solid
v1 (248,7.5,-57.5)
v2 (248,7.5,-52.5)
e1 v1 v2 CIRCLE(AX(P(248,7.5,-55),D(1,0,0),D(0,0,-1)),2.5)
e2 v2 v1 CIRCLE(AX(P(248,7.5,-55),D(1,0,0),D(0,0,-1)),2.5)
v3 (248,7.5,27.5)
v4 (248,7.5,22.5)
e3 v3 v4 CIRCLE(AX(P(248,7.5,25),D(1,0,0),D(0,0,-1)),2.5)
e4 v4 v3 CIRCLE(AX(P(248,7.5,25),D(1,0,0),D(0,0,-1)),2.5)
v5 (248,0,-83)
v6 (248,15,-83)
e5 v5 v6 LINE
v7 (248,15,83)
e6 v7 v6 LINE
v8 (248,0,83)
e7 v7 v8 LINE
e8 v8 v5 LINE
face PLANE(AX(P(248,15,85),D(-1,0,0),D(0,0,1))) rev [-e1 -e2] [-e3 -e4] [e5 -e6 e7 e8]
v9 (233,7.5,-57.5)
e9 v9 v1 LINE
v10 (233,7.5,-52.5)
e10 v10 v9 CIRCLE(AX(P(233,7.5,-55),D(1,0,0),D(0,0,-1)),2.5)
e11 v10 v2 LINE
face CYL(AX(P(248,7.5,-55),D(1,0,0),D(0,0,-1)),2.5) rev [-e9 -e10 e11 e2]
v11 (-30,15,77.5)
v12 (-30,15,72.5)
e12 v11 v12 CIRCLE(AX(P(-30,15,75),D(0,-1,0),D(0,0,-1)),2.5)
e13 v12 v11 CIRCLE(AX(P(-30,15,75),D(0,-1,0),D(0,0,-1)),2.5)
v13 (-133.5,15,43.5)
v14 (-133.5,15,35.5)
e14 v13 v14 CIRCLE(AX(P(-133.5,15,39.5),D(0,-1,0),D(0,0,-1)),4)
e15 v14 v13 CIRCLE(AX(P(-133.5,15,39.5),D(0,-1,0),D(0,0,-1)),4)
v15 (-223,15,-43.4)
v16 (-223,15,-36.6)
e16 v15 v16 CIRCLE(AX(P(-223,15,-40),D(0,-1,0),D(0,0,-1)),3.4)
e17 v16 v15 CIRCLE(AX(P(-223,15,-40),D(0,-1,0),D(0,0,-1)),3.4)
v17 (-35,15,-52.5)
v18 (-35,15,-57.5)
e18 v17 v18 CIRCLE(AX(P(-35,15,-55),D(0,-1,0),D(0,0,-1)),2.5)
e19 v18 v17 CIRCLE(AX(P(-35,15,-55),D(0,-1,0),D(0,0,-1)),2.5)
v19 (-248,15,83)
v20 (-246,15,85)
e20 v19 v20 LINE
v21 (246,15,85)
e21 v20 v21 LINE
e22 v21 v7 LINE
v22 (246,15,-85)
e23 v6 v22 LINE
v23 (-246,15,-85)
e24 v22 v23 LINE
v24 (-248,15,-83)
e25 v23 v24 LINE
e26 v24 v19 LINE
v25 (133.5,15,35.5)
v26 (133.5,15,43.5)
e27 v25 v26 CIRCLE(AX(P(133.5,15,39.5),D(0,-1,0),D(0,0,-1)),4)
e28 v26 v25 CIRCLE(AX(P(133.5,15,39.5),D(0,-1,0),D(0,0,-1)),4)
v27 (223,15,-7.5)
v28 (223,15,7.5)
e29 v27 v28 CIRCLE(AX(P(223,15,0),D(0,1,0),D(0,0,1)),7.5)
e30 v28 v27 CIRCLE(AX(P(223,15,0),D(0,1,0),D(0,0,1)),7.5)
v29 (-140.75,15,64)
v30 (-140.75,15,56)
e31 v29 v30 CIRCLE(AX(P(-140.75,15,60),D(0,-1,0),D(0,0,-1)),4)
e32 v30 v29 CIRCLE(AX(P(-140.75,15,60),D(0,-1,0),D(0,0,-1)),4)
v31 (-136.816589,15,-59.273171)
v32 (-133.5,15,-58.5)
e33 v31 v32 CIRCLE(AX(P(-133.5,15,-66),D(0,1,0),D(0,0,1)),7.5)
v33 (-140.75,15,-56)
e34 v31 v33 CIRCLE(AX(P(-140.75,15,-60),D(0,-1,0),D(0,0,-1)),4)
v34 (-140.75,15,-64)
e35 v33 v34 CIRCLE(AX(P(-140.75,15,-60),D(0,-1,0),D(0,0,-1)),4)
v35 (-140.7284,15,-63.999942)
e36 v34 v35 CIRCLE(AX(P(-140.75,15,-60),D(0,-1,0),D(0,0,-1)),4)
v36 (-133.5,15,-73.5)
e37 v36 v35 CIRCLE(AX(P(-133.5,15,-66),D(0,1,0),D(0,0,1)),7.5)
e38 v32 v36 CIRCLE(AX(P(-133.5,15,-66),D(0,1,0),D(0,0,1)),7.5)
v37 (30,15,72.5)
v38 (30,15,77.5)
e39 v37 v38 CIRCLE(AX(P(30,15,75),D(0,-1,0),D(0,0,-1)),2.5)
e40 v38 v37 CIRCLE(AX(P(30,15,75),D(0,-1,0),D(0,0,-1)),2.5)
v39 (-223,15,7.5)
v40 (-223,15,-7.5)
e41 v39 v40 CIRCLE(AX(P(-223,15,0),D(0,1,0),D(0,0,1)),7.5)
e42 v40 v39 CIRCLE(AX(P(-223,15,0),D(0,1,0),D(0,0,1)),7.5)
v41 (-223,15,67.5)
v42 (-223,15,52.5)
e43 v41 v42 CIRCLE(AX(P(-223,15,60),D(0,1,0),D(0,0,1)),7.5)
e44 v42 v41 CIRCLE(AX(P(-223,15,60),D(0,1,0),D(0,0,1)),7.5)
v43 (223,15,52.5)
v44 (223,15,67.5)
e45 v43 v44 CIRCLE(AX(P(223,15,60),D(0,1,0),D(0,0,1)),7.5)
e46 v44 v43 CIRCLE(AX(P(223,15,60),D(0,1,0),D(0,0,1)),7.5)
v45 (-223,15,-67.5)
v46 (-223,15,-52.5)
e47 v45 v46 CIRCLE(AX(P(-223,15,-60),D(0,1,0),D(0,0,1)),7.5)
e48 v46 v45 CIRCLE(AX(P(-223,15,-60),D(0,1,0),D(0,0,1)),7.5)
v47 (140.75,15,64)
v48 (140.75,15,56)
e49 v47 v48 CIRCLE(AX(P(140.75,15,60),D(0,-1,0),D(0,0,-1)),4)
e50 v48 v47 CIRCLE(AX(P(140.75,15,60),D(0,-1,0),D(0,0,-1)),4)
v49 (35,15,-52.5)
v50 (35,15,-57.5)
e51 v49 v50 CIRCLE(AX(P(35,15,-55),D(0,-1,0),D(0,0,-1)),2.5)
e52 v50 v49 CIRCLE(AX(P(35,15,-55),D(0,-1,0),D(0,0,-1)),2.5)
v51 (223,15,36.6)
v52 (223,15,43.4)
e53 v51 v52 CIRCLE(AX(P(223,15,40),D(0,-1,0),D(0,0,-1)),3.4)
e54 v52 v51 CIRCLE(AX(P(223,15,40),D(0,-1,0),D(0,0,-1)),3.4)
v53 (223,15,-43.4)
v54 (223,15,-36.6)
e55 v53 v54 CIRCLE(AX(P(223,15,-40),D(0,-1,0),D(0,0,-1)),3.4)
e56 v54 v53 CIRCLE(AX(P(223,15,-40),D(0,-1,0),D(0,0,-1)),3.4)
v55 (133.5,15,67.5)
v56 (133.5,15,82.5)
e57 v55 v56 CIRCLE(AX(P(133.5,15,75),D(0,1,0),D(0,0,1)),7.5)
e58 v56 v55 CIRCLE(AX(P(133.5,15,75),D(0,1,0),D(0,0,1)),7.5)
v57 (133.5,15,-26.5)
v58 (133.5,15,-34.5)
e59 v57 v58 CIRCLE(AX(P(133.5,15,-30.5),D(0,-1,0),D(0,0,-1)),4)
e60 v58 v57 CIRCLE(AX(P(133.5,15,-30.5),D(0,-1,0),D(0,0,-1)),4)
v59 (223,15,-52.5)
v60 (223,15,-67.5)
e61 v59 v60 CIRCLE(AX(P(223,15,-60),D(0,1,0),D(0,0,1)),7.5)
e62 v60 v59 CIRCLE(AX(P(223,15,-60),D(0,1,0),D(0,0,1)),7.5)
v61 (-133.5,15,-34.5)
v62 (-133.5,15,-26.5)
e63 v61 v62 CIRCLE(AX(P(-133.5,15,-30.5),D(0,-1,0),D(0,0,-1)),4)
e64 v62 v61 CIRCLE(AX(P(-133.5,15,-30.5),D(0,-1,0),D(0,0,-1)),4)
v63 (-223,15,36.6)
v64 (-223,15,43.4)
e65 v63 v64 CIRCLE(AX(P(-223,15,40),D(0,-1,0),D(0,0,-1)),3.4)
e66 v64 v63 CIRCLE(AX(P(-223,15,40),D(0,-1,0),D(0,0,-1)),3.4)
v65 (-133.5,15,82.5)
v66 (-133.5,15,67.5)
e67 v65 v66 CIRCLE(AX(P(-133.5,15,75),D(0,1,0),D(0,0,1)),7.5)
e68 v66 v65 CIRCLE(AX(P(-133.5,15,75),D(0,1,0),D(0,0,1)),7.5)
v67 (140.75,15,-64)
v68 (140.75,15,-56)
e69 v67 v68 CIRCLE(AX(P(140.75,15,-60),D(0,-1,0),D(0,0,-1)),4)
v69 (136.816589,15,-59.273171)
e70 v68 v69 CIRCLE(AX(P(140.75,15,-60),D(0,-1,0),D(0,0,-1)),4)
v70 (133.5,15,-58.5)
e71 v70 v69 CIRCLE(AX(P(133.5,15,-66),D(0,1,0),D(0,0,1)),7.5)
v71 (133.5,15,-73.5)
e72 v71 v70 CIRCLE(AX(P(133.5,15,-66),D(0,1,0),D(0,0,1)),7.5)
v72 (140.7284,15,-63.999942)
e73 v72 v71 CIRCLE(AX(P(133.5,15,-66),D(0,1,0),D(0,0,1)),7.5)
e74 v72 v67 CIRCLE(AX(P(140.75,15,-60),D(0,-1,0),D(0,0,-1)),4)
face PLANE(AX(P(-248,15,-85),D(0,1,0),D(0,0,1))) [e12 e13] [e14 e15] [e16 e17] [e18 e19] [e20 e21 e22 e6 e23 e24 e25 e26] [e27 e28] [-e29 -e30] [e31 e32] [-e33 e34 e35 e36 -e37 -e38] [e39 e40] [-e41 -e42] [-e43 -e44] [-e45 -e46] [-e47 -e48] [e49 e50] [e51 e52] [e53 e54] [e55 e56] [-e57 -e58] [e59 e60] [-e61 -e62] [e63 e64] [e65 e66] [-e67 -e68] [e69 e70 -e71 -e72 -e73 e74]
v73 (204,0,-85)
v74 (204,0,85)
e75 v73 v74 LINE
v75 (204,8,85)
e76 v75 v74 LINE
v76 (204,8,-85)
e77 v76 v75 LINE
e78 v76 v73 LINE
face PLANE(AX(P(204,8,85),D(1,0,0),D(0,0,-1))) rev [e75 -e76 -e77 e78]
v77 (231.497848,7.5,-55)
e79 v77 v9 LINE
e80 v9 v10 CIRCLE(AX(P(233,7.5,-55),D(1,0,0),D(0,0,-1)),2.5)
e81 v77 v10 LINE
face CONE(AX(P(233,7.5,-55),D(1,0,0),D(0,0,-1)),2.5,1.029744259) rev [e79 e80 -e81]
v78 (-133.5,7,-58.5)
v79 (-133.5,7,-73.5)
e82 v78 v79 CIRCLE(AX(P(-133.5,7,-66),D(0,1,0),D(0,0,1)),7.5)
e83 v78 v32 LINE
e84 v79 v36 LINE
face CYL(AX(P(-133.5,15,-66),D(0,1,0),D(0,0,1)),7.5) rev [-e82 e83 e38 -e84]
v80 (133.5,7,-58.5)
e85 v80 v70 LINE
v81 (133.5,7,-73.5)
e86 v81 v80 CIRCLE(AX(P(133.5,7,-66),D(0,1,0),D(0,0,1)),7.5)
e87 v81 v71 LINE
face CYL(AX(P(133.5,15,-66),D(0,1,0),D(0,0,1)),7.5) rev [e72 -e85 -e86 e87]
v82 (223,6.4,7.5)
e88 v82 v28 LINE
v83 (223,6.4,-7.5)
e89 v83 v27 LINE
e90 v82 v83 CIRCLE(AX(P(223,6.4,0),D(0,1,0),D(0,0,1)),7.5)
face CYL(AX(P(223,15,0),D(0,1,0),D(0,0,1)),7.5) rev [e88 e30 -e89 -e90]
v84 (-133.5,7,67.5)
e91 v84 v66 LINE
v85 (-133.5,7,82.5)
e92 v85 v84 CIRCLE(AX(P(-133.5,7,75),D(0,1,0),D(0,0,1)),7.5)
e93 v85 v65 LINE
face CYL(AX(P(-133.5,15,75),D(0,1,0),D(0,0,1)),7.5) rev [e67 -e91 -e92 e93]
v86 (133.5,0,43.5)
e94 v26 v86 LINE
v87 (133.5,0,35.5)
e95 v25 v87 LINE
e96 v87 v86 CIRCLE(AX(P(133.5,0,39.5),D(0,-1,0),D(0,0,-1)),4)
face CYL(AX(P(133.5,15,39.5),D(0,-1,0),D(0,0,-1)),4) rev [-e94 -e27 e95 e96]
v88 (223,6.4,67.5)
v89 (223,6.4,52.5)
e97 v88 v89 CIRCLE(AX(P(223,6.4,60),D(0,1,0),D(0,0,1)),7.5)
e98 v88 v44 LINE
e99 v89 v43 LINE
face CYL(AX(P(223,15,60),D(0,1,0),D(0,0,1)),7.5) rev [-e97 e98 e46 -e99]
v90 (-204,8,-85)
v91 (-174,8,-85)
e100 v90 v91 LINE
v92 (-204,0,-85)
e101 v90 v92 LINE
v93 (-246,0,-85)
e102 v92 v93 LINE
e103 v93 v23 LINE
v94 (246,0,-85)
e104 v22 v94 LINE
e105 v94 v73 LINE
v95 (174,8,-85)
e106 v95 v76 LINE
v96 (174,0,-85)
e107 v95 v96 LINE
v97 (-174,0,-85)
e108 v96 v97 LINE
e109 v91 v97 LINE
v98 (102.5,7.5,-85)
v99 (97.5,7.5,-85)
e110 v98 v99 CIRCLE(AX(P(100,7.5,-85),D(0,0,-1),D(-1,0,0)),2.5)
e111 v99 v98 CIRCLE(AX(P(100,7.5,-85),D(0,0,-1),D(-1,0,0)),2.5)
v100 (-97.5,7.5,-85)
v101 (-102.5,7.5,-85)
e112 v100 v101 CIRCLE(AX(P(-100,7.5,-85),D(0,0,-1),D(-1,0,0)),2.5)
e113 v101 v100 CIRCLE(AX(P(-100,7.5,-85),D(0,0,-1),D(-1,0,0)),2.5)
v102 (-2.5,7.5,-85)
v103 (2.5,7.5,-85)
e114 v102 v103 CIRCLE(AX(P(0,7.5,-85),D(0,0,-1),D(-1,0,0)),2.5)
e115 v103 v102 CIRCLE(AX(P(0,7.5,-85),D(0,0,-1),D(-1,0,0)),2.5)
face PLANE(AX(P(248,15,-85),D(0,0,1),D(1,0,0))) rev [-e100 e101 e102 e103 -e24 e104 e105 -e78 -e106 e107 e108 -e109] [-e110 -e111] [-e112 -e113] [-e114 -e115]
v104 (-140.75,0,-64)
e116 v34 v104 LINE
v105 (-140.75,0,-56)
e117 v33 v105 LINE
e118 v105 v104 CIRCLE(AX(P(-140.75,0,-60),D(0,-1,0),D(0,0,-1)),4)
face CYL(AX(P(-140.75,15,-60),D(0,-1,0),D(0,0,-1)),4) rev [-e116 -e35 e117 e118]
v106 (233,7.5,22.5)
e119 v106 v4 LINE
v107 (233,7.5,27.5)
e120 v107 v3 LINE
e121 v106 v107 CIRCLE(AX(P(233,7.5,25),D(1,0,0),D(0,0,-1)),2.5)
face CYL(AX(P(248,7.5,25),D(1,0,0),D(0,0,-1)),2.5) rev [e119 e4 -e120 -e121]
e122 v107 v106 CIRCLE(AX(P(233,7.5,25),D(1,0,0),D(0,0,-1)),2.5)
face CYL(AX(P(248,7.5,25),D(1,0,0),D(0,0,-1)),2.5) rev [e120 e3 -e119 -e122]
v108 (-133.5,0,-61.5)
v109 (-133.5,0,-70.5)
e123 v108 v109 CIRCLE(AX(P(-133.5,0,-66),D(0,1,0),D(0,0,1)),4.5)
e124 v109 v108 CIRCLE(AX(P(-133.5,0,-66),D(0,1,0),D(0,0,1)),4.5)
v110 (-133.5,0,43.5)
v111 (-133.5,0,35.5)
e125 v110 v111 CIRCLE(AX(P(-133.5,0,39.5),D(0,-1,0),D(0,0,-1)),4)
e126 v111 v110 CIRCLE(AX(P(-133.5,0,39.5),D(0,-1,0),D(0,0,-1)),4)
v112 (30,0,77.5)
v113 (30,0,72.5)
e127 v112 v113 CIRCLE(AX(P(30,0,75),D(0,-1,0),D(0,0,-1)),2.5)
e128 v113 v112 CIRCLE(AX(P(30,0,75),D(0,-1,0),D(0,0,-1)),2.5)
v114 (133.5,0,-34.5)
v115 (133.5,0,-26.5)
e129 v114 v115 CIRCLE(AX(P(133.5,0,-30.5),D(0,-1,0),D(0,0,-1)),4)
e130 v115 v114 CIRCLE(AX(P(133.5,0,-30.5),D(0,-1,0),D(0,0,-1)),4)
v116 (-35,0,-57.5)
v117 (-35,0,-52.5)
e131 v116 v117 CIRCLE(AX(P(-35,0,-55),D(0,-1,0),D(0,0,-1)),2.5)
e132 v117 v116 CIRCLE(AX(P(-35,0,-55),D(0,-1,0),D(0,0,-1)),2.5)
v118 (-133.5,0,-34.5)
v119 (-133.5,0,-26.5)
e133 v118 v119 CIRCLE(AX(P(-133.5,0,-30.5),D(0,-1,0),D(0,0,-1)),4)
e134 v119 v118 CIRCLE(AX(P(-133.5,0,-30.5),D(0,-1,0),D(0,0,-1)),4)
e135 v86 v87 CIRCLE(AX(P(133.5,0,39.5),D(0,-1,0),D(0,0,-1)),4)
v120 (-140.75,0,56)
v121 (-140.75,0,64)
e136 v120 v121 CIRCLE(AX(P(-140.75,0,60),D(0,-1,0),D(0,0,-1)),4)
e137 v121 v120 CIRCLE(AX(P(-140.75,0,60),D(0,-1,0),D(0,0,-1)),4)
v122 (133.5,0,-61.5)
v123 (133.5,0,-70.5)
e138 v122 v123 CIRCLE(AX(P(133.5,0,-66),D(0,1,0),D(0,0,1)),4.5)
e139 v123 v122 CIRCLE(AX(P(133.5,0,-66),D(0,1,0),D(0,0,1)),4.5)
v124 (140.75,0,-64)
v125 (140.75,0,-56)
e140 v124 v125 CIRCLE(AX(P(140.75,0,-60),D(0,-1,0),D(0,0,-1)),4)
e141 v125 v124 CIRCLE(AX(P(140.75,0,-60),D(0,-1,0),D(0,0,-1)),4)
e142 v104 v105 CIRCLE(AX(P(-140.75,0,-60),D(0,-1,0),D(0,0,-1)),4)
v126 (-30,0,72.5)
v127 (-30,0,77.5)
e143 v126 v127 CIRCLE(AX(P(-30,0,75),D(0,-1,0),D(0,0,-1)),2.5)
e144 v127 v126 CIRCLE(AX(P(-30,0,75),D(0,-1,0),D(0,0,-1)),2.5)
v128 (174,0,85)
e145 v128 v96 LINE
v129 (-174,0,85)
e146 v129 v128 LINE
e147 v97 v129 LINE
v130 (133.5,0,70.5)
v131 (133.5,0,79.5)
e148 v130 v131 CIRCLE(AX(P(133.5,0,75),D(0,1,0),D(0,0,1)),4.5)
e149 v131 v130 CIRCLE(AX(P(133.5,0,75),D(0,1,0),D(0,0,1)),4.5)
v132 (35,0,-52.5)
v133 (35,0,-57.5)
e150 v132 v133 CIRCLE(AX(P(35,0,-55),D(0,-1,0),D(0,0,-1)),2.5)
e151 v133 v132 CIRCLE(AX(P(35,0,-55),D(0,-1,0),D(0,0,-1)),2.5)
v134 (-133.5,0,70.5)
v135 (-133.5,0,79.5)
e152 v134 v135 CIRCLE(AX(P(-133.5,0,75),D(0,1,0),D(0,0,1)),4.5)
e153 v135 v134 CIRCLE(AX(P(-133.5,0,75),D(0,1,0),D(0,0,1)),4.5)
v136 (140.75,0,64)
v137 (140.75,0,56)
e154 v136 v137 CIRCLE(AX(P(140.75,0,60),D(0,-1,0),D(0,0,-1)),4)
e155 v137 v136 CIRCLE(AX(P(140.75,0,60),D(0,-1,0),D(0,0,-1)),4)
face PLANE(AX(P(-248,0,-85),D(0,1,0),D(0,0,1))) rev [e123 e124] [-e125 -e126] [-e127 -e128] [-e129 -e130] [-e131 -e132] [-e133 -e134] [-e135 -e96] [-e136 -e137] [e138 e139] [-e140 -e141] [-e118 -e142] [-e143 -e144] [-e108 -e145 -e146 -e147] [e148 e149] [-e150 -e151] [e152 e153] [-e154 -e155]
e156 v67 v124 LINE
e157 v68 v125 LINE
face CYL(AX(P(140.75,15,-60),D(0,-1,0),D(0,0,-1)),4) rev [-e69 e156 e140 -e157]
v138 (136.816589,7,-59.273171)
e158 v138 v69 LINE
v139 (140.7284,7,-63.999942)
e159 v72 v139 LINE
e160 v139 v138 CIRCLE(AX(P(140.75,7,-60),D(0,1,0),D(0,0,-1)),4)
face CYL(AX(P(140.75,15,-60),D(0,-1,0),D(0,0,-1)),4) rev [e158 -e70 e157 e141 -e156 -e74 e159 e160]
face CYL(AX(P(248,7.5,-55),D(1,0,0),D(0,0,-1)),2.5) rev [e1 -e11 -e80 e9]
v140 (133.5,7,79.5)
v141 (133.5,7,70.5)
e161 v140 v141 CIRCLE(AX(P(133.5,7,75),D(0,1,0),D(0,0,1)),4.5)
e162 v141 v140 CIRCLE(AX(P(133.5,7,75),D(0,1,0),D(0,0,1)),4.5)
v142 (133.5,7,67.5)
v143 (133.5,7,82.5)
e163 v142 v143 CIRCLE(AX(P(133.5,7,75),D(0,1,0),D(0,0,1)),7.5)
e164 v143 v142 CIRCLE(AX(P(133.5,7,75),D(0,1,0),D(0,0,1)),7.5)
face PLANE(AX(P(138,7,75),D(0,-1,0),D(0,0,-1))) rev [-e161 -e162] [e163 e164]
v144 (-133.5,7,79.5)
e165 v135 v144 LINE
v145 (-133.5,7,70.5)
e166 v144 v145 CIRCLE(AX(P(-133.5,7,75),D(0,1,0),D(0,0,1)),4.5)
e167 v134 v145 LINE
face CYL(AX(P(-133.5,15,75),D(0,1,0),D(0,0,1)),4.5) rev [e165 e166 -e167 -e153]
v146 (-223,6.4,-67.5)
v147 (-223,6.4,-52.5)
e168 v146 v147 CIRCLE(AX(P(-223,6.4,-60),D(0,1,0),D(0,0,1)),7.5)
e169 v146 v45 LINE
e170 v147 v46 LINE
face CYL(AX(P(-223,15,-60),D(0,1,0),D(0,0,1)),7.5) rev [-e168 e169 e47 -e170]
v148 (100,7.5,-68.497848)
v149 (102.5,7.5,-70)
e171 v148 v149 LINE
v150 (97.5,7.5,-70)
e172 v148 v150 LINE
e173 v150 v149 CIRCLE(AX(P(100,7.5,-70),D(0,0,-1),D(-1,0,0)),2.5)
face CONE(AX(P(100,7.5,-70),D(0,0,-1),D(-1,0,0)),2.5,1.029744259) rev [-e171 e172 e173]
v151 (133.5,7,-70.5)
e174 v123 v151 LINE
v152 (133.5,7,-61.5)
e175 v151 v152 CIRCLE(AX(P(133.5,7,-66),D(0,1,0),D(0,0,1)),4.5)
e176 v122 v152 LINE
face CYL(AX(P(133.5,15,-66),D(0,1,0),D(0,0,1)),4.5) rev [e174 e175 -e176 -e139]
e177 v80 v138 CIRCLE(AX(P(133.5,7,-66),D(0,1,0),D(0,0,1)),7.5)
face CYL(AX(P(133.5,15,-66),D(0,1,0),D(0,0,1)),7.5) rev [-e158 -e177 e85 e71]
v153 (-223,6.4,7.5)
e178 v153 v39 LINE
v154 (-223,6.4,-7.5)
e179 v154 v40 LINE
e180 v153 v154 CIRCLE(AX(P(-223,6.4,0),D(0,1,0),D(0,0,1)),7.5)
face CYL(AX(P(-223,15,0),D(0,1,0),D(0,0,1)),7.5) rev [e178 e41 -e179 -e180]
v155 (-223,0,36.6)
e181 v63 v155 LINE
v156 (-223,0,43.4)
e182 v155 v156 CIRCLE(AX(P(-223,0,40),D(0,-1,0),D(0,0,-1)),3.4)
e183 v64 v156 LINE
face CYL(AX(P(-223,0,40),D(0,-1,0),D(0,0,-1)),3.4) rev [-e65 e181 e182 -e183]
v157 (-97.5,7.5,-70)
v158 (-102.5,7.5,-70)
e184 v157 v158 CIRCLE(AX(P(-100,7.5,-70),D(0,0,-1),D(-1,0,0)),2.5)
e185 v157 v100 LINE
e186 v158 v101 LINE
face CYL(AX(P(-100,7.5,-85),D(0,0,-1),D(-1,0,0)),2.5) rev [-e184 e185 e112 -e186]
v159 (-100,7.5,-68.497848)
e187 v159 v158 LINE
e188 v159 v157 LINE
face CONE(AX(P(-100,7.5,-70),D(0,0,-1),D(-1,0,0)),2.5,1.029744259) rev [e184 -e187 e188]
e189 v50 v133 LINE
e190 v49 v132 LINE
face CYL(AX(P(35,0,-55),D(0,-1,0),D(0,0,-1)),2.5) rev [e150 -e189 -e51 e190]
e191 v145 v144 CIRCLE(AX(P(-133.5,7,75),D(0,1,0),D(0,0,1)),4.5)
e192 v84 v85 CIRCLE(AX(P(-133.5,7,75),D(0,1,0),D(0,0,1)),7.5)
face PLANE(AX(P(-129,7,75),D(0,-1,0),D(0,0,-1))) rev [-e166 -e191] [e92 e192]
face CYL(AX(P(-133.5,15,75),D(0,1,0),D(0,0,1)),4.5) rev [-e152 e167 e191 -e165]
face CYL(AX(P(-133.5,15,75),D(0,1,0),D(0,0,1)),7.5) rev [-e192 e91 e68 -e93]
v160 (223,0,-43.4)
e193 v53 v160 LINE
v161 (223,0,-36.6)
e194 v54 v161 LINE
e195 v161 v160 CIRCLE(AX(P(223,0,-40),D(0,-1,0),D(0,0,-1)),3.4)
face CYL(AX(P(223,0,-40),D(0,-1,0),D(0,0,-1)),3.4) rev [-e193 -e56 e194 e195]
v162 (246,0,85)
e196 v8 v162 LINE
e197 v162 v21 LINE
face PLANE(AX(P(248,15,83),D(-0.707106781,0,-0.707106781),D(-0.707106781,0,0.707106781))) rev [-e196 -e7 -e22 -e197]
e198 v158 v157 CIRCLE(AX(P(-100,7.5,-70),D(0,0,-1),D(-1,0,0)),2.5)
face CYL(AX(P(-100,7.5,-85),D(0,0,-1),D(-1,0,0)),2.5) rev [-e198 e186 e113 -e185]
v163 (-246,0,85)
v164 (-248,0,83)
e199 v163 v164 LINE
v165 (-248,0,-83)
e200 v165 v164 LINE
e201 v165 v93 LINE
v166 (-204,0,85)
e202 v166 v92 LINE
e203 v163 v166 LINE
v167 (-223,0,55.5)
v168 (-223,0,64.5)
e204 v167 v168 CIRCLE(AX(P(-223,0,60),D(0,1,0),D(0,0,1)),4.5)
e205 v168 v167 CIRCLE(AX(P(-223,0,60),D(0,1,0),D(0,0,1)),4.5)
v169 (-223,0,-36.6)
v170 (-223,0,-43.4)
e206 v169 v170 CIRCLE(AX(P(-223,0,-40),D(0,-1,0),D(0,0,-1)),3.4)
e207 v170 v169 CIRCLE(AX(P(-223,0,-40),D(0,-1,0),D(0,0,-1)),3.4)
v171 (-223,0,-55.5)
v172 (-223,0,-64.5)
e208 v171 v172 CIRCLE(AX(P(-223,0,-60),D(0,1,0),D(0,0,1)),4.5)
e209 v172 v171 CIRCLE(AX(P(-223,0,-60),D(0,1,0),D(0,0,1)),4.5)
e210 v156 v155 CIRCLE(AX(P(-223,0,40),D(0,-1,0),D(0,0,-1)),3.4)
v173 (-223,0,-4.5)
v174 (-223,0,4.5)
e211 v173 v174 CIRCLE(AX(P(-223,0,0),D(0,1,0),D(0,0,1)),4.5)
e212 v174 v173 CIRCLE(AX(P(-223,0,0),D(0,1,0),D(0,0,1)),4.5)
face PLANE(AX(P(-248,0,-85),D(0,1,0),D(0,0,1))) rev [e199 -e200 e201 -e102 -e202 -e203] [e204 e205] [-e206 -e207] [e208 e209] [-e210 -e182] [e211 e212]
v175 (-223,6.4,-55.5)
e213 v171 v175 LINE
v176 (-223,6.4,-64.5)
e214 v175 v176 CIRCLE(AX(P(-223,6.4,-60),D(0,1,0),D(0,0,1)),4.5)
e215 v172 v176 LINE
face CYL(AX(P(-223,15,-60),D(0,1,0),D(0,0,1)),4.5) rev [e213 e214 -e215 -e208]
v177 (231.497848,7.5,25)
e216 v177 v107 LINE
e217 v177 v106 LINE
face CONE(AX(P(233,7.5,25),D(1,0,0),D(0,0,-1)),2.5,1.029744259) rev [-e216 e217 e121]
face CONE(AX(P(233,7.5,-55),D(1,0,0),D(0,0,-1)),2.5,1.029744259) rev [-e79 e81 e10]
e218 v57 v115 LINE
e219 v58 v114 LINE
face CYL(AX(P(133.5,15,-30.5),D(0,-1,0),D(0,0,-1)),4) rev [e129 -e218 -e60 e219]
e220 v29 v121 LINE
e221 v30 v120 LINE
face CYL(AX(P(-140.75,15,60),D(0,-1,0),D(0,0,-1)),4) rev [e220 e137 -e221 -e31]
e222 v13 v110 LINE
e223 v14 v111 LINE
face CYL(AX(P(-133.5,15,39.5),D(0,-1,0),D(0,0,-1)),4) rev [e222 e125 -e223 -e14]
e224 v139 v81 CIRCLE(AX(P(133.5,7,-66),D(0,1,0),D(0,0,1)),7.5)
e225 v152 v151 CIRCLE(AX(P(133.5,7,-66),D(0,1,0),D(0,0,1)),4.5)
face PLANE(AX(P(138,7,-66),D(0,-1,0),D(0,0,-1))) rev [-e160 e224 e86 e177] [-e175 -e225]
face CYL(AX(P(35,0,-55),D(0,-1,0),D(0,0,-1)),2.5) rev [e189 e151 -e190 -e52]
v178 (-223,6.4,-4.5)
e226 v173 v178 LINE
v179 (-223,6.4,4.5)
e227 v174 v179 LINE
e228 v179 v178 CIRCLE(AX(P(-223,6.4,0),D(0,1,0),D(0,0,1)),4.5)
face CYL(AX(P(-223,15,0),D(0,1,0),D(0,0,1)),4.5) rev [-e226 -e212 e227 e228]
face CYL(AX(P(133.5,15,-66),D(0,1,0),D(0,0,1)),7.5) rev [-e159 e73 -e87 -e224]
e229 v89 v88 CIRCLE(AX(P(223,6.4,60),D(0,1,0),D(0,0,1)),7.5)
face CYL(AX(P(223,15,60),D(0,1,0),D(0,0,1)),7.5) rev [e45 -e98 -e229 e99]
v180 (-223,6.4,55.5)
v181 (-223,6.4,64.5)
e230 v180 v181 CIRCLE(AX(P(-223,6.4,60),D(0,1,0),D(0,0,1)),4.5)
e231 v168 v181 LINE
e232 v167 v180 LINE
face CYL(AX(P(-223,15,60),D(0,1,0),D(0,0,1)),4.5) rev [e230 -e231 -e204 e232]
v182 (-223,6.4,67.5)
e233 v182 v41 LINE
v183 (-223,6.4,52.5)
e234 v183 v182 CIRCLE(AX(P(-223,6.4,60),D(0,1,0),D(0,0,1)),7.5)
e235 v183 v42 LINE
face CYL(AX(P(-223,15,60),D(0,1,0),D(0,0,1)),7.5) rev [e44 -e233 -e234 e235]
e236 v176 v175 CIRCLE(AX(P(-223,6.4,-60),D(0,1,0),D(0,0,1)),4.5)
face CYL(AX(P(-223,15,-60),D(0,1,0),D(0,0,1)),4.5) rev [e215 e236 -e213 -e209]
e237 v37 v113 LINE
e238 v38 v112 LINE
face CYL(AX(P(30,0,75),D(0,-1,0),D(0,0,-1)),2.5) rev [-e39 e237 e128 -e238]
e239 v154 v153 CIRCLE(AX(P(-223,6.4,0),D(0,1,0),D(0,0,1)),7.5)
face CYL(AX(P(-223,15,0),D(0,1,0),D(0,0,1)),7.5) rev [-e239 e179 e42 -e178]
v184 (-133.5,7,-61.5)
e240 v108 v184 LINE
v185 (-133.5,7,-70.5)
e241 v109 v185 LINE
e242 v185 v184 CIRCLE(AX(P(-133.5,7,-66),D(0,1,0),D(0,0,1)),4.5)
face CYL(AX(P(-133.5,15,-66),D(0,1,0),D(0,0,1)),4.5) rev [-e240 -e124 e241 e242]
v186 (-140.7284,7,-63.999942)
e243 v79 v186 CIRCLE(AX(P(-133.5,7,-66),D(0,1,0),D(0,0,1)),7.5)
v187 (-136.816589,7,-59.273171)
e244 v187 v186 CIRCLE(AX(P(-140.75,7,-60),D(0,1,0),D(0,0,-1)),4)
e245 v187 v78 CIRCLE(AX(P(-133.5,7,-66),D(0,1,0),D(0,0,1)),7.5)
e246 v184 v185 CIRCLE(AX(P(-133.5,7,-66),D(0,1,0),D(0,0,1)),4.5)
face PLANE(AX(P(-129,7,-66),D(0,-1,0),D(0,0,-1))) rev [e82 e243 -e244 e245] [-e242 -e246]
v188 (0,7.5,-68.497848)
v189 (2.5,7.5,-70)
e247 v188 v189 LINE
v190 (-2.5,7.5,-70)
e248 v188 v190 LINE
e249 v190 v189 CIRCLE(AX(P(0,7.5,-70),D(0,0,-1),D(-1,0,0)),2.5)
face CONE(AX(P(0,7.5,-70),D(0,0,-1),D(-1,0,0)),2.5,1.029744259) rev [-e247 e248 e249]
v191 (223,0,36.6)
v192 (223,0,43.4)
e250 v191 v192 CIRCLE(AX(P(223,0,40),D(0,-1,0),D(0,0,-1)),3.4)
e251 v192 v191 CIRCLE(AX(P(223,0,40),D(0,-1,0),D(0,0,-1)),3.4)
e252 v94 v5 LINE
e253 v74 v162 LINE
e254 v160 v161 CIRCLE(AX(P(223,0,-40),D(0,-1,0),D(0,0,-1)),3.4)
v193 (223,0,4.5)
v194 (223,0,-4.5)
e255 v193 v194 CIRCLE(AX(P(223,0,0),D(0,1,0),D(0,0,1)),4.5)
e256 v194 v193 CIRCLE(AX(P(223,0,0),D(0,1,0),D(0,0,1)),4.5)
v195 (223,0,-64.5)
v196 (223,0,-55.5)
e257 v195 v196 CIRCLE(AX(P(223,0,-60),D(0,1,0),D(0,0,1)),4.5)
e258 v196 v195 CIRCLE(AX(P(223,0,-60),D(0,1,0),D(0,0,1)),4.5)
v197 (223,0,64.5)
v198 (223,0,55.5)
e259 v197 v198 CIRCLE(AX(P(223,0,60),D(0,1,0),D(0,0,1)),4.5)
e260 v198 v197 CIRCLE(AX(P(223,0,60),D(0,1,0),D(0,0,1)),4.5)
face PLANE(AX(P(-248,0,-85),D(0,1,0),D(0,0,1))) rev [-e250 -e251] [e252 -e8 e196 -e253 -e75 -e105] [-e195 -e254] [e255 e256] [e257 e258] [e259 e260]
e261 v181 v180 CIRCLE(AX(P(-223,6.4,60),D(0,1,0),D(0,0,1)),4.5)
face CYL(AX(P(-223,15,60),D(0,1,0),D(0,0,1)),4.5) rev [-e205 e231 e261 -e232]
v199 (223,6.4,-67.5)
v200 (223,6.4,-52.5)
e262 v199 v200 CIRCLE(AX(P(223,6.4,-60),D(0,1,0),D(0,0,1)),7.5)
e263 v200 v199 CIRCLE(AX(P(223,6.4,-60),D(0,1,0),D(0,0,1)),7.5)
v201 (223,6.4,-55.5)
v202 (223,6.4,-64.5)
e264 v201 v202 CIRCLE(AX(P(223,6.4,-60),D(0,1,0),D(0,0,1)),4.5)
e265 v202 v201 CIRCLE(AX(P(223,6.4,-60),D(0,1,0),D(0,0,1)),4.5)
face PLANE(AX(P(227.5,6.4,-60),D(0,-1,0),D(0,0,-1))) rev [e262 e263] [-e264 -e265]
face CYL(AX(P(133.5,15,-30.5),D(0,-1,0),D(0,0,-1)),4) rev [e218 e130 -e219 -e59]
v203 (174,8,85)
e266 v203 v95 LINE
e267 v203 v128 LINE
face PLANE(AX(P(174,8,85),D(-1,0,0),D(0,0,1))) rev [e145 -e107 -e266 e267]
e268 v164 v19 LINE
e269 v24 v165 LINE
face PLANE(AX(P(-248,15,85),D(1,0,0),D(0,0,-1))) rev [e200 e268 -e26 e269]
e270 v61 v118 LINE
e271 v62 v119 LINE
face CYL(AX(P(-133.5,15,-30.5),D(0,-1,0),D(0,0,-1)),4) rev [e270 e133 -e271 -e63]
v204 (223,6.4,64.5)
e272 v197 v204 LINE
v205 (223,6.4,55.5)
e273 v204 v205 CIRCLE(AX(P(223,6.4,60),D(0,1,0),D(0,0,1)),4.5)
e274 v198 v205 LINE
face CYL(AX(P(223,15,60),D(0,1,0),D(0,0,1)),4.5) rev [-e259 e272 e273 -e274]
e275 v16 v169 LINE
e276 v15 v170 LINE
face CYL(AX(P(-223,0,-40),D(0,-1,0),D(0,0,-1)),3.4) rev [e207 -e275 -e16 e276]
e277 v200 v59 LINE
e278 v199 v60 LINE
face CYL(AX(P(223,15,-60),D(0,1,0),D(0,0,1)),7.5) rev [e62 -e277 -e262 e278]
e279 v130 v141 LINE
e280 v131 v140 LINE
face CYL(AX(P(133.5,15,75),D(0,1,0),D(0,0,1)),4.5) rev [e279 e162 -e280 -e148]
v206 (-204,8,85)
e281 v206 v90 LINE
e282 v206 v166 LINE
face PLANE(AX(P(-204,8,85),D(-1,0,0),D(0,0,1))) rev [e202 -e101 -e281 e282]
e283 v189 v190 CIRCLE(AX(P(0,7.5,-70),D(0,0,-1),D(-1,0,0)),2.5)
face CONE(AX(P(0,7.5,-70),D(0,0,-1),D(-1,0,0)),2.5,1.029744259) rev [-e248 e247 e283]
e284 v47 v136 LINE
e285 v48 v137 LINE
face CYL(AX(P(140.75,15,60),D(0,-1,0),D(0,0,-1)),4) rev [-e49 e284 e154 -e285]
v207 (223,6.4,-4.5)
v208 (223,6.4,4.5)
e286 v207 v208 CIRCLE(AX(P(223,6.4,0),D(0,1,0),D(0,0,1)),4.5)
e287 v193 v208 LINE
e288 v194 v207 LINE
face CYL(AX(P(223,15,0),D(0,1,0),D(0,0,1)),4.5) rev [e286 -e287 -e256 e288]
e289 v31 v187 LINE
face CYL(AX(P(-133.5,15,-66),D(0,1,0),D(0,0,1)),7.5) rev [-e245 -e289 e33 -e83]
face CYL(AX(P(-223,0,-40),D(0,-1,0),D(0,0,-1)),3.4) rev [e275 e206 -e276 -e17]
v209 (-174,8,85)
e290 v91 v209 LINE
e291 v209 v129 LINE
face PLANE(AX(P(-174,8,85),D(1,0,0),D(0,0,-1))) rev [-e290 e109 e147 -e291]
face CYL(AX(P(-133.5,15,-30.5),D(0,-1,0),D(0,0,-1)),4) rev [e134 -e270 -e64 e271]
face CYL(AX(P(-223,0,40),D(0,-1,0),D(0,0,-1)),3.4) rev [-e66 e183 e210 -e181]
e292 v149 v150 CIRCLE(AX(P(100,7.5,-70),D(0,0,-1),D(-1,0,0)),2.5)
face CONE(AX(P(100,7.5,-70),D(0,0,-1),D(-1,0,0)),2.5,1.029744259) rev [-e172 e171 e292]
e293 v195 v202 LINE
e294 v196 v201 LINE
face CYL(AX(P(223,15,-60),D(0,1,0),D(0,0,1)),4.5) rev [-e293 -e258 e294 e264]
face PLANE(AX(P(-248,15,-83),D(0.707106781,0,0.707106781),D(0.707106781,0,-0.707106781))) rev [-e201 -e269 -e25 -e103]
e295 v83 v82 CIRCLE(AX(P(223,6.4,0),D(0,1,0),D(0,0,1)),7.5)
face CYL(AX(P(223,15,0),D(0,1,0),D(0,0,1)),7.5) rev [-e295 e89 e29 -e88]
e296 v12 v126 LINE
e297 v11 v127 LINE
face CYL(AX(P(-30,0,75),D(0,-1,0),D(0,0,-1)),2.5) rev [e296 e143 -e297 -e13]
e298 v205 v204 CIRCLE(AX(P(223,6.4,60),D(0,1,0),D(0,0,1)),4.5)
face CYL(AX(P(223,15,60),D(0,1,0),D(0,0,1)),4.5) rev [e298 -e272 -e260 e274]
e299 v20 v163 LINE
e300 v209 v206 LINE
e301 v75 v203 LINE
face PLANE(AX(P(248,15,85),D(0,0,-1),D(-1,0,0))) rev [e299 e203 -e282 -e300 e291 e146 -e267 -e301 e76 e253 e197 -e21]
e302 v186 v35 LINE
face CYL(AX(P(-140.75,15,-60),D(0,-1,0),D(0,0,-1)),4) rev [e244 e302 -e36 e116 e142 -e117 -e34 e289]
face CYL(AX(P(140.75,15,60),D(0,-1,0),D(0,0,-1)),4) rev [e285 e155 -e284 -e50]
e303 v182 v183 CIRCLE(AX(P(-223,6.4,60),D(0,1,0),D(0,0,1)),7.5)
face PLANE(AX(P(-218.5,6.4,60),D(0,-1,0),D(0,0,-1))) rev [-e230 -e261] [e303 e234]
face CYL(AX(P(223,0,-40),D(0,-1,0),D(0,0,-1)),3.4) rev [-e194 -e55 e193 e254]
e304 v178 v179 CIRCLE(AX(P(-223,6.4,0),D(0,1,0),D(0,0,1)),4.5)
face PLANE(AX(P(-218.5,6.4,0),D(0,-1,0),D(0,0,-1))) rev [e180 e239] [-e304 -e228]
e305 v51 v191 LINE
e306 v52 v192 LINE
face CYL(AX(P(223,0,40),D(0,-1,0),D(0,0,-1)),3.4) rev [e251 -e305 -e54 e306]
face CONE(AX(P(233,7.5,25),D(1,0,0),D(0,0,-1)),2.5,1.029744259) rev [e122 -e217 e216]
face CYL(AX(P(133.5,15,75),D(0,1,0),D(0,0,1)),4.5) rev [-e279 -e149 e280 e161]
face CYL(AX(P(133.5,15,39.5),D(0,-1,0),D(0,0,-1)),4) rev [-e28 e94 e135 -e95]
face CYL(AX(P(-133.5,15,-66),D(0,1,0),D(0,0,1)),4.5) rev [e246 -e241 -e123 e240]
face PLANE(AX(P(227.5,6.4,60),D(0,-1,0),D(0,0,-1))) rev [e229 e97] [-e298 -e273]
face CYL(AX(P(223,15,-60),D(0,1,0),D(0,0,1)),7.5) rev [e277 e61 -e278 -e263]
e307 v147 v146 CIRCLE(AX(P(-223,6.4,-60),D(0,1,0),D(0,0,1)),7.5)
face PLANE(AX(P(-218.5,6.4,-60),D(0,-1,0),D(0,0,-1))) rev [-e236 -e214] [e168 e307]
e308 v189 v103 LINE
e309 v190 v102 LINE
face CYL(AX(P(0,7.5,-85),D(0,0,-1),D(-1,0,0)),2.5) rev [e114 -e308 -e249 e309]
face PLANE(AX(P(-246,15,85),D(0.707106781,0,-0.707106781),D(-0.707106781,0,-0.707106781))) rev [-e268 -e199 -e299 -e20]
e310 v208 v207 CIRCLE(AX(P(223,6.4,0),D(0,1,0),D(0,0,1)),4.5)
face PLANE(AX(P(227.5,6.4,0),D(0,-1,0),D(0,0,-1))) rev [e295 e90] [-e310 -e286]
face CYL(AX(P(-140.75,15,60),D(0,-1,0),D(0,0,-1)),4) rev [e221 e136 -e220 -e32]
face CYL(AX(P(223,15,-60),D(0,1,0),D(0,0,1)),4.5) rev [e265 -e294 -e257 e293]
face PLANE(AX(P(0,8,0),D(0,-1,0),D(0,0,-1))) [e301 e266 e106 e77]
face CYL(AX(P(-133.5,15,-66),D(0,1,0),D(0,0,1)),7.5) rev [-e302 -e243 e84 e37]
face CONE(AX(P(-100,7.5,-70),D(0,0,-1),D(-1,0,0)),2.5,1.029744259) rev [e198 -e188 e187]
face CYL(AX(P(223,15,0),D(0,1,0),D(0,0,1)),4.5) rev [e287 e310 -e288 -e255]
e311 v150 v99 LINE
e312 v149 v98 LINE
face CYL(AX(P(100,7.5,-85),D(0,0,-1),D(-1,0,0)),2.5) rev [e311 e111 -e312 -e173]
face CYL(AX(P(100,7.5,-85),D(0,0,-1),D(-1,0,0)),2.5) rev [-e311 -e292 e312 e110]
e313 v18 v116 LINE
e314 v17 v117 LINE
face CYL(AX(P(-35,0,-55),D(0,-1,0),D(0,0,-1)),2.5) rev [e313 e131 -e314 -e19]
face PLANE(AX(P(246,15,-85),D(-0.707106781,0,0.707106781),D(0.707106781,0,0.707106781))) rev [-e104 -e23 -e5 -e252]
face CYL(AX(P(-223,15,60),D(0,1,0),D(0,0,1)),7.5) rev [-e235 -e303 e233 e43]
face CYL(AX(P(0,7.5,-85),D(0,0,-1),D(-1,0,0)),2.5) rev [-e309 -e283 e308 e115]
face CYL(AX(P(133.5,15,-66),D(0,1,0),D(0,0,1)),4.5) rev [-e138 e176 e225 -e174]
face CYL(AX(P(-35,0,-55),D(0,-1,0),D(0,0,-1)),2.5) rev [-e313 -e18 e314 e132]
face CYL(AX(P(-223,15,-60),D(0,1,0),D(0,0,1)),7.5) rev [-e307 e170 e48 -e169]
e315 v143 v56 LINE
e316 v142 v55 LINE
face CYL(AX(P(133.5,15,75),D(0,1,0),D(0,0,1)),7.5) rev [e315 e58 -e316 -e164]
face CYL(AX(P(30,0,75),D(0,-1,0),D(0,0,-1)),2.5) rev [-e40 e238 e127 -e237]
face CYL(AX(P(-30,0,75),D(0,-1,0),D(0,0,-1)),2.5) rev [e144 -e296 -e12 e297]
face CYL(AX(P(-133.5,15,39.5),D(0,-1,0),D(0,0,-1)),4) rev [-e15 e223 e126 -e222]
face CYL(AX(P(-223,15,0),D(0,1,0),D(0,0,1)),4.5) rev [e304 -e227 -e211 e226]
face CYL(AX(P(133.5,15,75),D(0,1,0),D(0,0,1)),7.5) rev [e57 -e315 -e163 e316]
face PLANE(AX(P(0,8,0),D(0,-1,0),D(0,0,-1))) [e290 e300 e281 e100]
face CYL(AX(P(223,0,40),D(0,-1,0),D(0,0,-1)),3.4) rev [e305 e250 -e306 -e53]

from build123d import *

# Parameters (mm, degrees)
SKETCH1_W                                           = 496
SKETCH1_H                                           = 170
BOSS_EXTRUDE1_DEPTH                                 = 15
CBORE_FOR_M8_HEX_SOCKET_HEAD_CAP_SCREW2_D           = 9
CBORE_FOR_M8_HEX_SOCKET_HEAD_CAP_SCREW2_CBORE_D     = 15
CBORE_FOR_M8_HEX_SOCKET_HEAD_CAP_SCREW2_CBORE_DEPTH = 8.6
SKETCH4_R                                           = 4
CUT_EXTRUDE1_DEPTH                                  = 263.59093663
SKETCH5_R                                           = 4
CUT_EXTRUDE2_DEPTH                                  = 263.59093663
CBORE_FOR_M8_HEX_SOCKET_HEAD_CAP_SCREW1_D           = 9
CBORE_FOR_M8_HEX_SOCKET_HEAD_CAP_SCREW1_CBORE_D     = 15
CBORE_FOR_M8_HEX_SOCKET_HEAD_CAP_SCREW1_CBORE_DEPTH = 8
M6_TAPPED_HOLE1_D                                   = 5
M6_TAPPED_HOLE1_DEPTH                               = 15
M6_TAPPED_HOLE1_TIP                                 = 1.502151548
M6_TAPPED_HOLE2_D                                   = 5
CHAMFER1_SIZE                                       = 2
M6_TAPPED_HOLE3_D                                   = 5
M6_TAPPED_HOLE4_D                                   = 5
M6_TAPPED_HOLE4_DEPTH                               = 15
M6_TAPPED_HOLE4_TIP                                 = 1.502151548
M8_TAPPED_HOLE1_D                                   = 6.8
SKETCH18_W                                          = 30
SKETCH18_H                                          = 170
CUT_EXTRUDE3_DEPTH                                  = 8


with BuildPart() as part:
    # Sketch1 → Boss-Extrude1 (new body)
    with BuildSketch(Plane(origin=(0, 0, 0), x_dir=(1, 0, 0), z_dir=(0, 1, 0))):
        Rectangle(SKETCH1_W, SKETCH1_H)
    extrude(amount=BOSS_EXTRUDE1_DEPTH)

    # CBORE for M8 Hex Socket Head Cap Screw2 (through all)
    with Locations(Plane(origin=(0, 15, 0), x_dir=(-1, 0, 0), z_dir=(0, 1, 0))):
        with Locations((223, -60), (223, 0), (223, 60)):
            cbore_for_m8_hex_socket_head_cap_screw2 = CounterBoreHole(CBORE_FOR_M8_HEX_SOCKET_HEAD_CAP_SCREW2_D / 2, CBORE_FOR_M8_HEX_SOCKET_HEAD_CAP_SCREW2_CBORE_D / 2, CBORE_FOR_M8_HEX_SOCKET_HEAD_CAP_SCREW2_CBORE_DEPTH)

    # Sketch4 → Cut-Extrude1 (cut, through all)
    with BuildSketch(Plane.XZ):
        with Locations(Location((140.75, 60, 0), (0, 0, 270))):
            Circle(SKETCH4_R)
        with Locations(Location((140.75, -60, 0), (0, 0, 270))):
            Circle(SKETCH4_R)
        with Locations(Location((-140.75, -60, 0), (0, 0, 270))):
            Circle(SKETCH4_R)
        with Locations(Location((-140.75, 60, 0), (0, 0, 270))):
            Circle(SKETCH4_R)
    extrude(amount=-CUT_EXTRUDE1_DEPTH, mode=Mode.SUBTRACT)

    # Sketch5 → Cut-Extrude2 (cut, through all)
    with BuildSketch(Plane.XZ):
        with Locations(Location((133.5, -30.5, 0), (0, 0, 270))):
            Circle(SKETCH5_R)
        with Locations(Location((133.5, 39.5, 0), (0, 0, 270))):
            Circle(SKETCH5_R)
        with Locations(Location((-133.5, 39.5, 0), (0, 0, 270))):
            Circle(SKETCH5_R)
        with Locations(Location((-133.5, -30.5, 0), (0, 0, 270))):
            Circle(SKETCH5_R)
    extrude(amount=-CUT_EXTRUDE2_DEPTH, mode=Mode.SUBTRACT)

    # CBORE for M8 Hex Socket Head Cap Screw1 (through all)
    with Locations(Plane(origin=(0, 15, 0), x_dir=(-1, 0, 0), z_dir=(0, 1, 0))):
        with Locations((133.5, -66), (-133.5, -66), (133.5, 75), (-133.5, 75)):
            CounterBoreHole(CBORE_FOR_M8_HEX_SOCKET_HEAD_CAP_SCREW1_D / 2, CBORE_FOR_M8_HEX_SOCKET_HEAD_CAP_SCREW1_CBORE_D / 2, CBORE_FOR_M8_HEX_SOCKET_HEAD_CAP_SCREW1_CBORE_DEPTH)

    # M6 Tapped Hole1
    with Locations(Plane(origin=(248, 0, 0), x_dir=(0, 0, -1), z_dir=(1, 0, 0))):
        with Locations((55, 7.5), (-25, 7.5)):
            Hole(M6_TAPPED_HOLE1_D / 2, depth=M6_TAPPED_HOLE1_DEPTH)
            with Locations((0, 0, -(M6_TAPPED_HOLE1_DEPTH + M6_TAPPED_HOLE1_TIP / 2))):  # 118° drill point
                Cone(0, M6_TAPPED_HOLE1_D / 2, M6_TAPPED_HOLE1_TIP, mode=Mode.SUBTRACT)

    # M6 Tapped Hole2 (through all)
    with Locations(Plane.XZ):
        with Locations((-35, -55), (35, -55)):
            Hole(M6_TAPPED_HOLE2_D / 2)

    # Chamfer1
    chamfer1_edges = [part.edges().sort_by_distance(p)[0] for p in [
        (248, 7.5, 85),
        (-248, 7.5, 85),
        (248, 7.5, -85),
        (-248, 7.5, -85),
    ]]
    chamfer(chamfer1_edges, length=CHAMFER1_SIZE)

    # M6 Tapped Hole3 (through all)
    with Locations(Plane.XZ):
        with Locations((-30, 75), (30, 75)):
            Hole(M6_TAPPED_HOLE3_D / 2)

    # M6 Tapped Hole4
    with Locations(Plane(origin=(0, 0, -85), x_dir=(-1, 0, 0), z_dir=(0, 0, -1))):
        with Locations((0, 7.5), (100, 7.5), (-100, 7.5)):
            Hole(M6_TAPPED_HOLE4_D / 2, depth=M6_TAPPED_HOLE4_DEPTH)
            with Locations((0, 0, -(M6_TAPPED_HOLE4_DEPTH + M6_TAPPED_HOLE4_TIP / 2))):  # 118° drill point
                Cone(0, M6_TAPPED_HOLE4_D / 2, M6_TAPPED_HOLE4_TIP, mode=Mode.SUBTRACT)

    # Mirror1: CBORE for M8 Hex Socket Head Cap Screw2 across plane
    add(cbore_for_m8_hex_socket_head_cap_screw2.mirror(Plane(origin=(0, 0, 0), x_dir=(0, 0, 1), z_dir=(1, 0, 0))), mode=Mode.SUBTRACT)

    # M8 Tapped Hole1 (through all)
    with Locations(Plane.XZ):
        with Locations((-223, 40), (-223, -40), (223, -40), (223, 40)):
            Hole(M8_TAPPED_HOLE1_D / 2)

    # Sketch18 → Cut-Extrude3 (cut)
    with BuildSketch(Plane.XZ):
        with Locations((-189, 0)):
            Rectangle(SKETCH18_W, SKETCH18_H)
        with Locations((189, 0)):
            Rectangle(SKETCH18_W, SKETCH18_H)
    extrude(amount=-CUT_EXTRUDE3_DEPTH, mode=Mode.SUBTRACT)


solid = part.part
